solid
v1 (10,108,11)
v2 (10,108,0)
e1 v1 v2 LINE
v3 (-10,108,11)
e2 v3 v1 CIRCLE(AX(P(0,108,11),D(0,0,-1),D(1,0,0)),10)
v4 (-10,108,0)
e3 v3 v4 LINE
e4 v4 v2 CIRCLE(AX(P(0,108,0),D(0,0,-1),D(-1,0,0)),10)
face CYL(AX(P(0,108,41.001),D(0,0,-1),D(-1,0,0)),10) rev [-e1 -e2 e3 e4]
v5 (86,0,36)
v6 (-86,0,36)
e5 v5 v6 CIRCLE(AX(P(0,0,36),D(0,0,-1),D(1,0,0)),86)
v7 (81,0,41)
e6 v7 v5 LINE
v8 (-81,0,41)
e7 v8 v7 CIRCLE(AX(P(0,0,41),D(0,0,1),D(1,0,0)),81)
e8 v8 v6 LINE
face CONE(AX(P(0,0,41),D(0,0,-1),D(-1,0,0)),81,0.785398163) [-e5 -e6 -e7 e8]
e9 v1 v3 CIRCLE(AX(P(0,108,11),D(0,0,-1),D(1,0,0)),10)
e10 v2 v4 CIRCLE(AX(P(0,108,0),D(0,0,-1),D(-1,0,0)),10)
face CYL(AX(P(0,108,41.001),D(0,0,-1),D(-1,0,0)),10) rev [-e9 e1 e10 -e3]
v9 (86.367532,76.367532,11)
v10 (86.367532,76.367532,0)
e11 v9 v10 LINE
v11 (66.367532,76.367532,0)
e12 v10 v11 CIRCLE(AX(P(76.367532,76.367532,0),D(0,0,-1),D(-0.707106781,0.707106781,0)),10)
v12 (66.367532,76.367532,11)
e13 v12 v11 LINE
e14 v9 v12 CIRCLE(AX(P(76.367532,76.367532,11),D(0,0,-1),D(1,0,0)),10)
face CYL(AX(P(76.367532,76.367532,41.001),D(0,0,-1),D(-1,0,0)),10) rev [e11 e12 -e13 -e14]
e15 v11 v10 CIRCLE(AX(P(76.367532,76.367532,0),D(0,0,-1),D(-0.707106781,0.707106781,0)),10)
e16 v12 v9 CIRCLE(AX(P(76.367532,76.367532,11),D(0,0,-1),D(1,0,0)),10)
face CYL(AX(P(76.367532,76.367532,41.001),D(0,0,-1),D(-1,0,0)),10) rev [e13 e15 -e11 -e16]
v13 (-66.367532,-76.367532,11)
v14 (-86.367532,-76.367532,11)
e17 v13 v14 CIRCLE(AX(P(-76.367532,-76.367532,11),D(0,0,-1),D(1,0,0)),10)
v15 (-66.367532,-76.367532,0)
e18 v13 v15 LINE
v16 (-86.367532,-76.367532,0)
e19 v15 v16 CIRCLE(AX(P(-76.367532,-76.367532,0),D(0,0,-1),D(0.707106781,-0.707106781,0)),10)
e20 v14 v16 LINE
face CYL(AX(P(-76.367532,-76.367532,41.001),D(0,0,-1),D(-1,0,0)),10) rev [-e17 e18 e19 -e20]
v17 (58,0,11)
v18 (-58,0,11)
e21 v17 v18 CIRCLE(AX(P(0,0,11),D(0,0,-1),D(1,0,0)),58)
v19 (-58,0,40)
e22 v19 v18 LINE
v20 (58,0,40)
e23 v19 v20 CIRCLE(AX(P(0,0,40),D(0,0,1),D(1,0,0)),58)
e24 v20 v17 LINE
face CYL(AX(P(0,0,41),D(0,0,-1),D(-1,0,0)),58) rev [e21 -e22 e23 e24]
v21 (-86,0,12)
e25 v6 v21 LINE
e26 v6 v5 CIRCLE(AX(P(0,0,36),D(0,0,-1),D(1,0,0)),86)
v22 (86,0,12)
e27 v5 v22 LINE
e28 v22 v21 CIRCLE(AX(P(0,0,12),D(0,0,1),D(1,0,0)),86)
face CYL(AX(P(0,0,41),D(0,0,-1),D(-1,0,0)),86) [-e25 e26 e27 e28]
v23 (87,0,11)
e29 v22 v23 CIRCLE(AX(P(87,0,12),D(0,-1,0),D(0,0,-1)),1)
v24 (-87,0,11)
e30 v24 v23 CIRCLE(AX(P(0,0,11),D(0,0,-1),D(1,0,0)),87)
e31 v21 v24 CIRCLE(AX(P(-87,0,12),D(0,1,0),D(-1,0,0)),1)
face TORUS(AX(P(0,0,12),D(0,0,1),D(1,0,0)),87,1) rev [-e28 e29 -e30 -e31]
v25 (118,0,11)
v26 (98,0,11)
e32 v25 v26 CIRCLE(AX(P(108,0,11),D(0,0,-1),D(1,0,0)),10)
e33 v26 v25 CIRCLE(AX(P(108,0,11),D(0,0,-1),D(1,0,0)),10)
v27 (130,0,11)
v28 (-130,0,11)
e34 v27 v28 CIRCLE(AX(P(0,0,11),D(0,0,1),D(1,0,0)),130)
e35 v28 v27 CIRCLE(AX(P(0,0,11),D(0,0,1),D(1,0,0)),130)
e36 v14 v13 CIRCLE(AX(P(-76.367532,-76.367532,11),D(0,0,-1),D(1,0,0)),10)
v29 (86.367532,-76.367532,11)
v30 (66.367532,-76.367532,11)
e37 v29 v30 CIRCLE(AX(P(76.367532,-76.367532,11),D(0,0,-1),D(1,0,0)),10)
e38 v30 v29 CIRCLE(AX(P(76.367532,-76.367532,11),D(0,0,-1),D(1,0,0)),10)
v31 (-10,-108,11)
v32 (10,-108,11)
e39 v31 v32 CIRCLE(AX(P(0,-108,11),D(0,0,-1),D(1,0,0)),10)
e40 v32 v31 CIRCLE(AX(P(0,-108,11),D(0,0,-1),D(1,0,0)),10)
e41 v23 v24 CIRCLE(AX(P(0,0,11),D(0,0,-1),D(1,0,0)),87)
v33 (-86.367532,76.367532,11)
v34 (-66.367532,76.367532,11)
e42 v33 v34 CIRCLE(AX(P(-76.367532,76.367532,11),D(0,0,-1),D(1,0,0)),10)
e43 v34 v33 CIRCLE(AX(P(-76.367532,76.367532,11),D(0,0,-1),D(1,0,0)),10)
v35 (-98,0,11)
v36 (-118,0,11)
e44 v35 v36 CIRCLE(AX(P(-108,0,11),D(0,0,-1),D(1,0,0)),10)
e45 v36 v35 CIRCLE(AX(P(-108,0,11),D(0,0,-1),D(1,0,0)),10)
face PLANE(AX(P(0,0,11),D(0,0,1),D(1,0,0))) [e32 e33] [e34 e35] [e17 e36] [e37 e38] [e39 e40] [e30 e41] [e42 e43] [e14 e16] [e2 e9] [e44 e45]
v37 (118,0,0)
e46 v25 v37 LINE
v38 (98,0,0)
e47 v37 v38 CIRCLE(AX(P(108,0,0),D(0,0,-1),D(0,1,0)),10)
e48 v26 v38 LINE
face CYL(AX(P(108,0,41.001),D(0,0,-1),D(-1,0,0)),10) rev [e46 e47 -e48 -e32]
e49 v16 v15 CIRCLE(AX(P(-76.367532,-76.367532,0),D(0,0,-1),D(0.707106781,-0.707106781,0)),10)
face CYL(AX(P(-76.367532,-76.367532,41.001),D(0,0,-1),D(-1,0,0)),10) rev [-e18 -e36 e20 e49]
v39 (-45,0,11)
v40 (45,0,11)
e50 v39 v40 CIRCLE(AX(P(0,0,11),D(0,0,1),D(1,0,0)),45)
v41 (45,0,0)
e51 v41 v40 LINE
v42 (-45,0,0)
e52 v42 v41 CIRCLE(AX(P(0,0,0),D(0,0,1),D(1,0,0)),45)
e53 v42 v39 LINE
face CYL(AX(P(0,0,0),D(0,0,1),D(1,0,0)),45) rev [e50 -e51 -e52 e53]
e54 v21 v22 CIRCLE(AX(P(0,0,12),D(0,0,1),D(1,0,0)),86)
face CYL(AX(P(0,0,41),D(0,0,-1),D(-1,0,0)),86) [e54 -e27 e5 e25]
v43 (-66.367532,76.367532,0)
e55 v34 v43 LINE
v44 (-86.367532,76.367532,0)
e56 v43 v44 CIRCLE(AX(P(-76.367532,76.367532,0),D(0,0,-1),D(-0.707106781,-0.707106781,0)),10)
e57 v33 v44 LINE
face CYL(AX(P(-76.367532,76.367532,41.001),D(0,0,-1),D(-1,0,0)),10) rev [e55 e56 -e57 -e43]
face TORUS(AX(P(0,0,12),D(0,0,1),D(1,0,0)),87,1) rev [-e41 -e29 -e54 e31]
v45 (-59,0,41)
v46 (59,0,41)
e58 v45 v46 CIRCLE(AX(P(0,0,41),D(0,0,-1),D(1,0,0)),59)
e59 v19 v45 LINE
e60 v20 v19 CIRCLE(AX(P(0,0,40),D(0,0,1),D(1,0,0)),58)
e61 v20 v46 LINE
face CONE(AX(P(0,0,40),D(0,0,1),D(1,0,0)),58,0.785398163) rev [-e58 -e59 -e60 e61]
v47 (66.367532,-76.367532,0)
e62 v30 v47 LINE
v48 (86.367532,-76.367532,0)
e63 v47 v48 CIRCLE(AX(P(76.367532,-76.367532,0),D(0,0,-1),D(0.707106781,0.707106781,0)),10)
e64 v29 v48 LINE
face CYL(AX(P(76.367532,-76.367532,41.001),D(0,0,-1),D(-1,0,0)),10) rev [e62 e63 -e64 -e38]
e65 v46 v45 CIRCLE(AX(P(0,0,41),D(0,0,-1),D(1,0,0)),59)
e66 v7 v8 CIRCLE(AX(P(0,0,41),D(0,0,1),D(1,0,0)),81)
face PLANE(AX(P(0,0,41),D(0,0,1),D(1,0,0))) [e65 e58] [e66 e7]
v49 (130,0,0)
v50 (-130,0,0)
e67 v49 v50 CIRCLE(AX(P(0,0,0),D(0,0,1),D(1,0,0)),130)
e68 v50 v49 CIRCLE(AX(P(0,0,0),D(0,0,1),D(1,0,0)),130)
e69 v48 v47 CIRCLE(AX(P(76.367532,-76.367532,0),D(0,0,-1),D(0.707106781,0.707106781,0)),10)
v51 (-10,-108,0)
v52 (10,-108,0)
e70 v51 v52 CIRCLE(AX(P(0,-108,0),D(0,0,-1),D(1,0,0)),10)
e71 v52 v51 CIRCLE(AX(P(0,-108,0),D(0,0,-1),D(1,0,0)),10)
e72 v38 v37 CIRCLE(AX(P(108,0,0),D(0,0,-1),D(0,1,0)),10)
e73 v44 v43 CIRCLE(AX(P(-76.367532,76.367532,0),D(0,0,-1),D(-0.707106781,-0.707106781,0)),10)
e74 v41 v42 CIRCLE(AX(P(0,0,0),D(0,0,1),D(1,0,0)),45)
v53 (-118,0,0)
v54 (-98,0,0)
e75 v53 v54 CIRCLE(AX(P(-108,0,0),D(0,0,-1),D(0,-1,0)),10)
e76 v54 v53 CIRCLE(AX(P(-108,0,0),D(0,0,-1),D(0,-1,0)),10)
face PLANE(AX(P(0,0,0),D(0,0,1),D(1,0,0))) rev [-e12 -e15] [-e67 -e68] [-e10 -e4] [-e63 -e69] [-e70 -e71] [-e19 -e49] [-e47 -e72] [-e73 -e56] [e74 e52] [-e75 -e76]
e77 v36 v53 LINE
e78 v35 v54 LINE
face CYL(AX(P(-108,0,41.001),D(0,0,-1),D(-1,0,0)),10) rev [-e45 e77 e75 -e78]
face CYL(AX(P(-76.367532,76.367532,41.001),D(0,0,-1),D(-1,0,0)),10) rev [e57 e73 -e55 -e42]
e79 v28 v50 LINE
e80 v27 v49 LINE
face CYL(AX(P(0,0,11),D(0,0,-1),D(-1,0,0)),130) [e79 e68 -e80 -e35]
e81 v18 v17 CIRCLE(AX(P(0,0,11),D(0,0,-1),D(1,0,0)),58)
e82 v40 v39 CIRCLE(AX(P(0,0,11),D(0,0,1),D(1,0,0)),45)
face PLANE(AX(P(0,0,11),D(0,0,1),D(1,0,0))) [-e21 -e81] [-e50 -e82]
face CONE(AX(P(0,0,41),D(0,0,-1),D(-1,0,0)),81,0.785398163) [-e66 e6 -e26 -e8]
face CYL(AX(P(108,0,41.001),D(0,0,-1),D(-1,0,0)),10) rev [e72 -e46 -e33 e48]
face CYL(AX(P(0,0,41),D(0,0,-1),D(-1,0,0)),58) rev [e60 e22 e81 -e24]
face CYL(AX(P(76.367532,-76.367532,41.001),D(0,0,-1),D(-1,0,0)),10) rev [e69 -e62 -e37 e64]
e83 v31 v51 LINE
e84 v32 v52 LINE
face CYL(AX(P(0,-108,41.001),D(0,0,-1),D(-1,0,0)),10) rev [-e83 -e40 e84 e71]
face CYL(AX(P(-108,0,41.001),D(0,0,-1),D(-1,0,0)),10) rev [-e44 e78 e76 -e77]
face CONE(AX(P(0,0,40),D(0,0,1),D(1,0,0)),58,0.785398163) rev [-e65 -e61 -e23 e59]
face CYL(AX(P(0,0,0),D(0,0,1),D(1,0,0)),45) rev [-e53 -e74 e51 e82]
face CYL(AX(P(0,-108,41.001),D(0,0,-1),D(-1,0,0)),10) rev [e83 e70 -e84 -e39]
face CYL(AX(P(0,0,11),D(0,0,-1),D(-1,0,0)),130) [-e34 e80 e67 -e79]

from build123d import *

# Parameters (mm, degrees)
SKETCH_1_R               = 130
EXTRUDE_1_DEPTH          = 11
SKETCH_2_R               = 86
SKETCH_2_R_2             = 58
EXTRUDE_2_DEPTH          = 30
FILLET_1_R               = 1
CHAMFER_1_SIZE           = 1
CHAMFER_2_SIZE           = 5
CUT_EXTRUDE_1_REACH      = 190.364
SKETCH_4_R               = 10
PATTERN_CIRCULAR_1_COUNT = 8
SKETCH_5_R               = 45
CUT_EXTRUDE_2_DEPTH      = 187.279360102


with BuildPart() as part:
    # 草图1 → 凸台-拉伸1 (new body)
    with BuildSketch(Plane.XY):
        Circle(SKETCH_1_R)
    extrude(amount=EXTRUDE_1_DEPTH)

    # 草图2 → 凸台-拉伸2 (add)
    with BuildSketch(Plane.XY.offset(11)):
        Circle(SKETCH_2_R)
        Circle(SKETCH_2_R_2, mode=Mode.SUBTRACT)
    extrude(amount=EXTRUDE_2_DEPTH)

    # 圆角1
    fillet_1_edges = [part.edges().sort_by_distance(p)[0] for p in [
        (-86, 0, 11),
    ]]
    fillet(fillet_1_edges, radius=FILLET_1_R)

    # 倒角1
    chamfer_1_edges = [part.edges().sort_by_distance(p)[0] for p in [
        (-58, 0, 41),
    ]]
    chamfer(chamfer_1_edges, length=CHAMFER_1_SIZE)

    # 倒角2
    chamfer_2_edges = [part.edges().sort_by_distance(p)[0] for p in [
        (-86, 0, 41),
    ]]
    chamfer(chamfer_2_edges, length=CHAMFER_2_SIZE)

    # 草图4 → 切除-拉伸1 (cut, up to next)
    with BuildSketch(Plane(origin=(0, 0, 0), x_dir=(-1, 0, 0), z_dir=(0, 0, -1)), mode=Mode.PRIVATE) as cut_extrude_1_sk1:
        with Locations((0, 108)):
            Circle(SKETCH_4_R)
    cut_extrude_1_tool1 = extrude(cut_extrude_1_sk1.sketch, amount=-CUT_EXTRUDE_1_REACH, mode=Mode.PRIVATE) & part.part
    cut_extrude_1 = cut_extrude_1_tool1.solids().sort_by_distance((0, 108, 0))[0]
    add(cut_extrude_1, mode=Mode.SUBTRACT)

    # 阵列(圆周)1: 切除-拉伸1 ×8 about axis
    pattern_circular_1_axis = Axis((0, 0, 0), (0, 0, 1))
    for i in range(1, PATTERN_CIRCULAR_1_COUNT):
        add(cut_extrude_1.rotate(pattern_circular_1_axis, i * 360 / PATTERN_CIRCULAR_1_COUNT), mode=Mode.SUBTRACT)

    # 草图5 → 切除-拉伸2 (cut, through all)
    with BuildSketch(Plane.XY.offset(11)):
        Circle(SKETCH_5_R)
    extrude(amount=-CUT_EXTRUDE_2_DEPTH, mode=Mode.SUBTRACT)


solid = part.part
